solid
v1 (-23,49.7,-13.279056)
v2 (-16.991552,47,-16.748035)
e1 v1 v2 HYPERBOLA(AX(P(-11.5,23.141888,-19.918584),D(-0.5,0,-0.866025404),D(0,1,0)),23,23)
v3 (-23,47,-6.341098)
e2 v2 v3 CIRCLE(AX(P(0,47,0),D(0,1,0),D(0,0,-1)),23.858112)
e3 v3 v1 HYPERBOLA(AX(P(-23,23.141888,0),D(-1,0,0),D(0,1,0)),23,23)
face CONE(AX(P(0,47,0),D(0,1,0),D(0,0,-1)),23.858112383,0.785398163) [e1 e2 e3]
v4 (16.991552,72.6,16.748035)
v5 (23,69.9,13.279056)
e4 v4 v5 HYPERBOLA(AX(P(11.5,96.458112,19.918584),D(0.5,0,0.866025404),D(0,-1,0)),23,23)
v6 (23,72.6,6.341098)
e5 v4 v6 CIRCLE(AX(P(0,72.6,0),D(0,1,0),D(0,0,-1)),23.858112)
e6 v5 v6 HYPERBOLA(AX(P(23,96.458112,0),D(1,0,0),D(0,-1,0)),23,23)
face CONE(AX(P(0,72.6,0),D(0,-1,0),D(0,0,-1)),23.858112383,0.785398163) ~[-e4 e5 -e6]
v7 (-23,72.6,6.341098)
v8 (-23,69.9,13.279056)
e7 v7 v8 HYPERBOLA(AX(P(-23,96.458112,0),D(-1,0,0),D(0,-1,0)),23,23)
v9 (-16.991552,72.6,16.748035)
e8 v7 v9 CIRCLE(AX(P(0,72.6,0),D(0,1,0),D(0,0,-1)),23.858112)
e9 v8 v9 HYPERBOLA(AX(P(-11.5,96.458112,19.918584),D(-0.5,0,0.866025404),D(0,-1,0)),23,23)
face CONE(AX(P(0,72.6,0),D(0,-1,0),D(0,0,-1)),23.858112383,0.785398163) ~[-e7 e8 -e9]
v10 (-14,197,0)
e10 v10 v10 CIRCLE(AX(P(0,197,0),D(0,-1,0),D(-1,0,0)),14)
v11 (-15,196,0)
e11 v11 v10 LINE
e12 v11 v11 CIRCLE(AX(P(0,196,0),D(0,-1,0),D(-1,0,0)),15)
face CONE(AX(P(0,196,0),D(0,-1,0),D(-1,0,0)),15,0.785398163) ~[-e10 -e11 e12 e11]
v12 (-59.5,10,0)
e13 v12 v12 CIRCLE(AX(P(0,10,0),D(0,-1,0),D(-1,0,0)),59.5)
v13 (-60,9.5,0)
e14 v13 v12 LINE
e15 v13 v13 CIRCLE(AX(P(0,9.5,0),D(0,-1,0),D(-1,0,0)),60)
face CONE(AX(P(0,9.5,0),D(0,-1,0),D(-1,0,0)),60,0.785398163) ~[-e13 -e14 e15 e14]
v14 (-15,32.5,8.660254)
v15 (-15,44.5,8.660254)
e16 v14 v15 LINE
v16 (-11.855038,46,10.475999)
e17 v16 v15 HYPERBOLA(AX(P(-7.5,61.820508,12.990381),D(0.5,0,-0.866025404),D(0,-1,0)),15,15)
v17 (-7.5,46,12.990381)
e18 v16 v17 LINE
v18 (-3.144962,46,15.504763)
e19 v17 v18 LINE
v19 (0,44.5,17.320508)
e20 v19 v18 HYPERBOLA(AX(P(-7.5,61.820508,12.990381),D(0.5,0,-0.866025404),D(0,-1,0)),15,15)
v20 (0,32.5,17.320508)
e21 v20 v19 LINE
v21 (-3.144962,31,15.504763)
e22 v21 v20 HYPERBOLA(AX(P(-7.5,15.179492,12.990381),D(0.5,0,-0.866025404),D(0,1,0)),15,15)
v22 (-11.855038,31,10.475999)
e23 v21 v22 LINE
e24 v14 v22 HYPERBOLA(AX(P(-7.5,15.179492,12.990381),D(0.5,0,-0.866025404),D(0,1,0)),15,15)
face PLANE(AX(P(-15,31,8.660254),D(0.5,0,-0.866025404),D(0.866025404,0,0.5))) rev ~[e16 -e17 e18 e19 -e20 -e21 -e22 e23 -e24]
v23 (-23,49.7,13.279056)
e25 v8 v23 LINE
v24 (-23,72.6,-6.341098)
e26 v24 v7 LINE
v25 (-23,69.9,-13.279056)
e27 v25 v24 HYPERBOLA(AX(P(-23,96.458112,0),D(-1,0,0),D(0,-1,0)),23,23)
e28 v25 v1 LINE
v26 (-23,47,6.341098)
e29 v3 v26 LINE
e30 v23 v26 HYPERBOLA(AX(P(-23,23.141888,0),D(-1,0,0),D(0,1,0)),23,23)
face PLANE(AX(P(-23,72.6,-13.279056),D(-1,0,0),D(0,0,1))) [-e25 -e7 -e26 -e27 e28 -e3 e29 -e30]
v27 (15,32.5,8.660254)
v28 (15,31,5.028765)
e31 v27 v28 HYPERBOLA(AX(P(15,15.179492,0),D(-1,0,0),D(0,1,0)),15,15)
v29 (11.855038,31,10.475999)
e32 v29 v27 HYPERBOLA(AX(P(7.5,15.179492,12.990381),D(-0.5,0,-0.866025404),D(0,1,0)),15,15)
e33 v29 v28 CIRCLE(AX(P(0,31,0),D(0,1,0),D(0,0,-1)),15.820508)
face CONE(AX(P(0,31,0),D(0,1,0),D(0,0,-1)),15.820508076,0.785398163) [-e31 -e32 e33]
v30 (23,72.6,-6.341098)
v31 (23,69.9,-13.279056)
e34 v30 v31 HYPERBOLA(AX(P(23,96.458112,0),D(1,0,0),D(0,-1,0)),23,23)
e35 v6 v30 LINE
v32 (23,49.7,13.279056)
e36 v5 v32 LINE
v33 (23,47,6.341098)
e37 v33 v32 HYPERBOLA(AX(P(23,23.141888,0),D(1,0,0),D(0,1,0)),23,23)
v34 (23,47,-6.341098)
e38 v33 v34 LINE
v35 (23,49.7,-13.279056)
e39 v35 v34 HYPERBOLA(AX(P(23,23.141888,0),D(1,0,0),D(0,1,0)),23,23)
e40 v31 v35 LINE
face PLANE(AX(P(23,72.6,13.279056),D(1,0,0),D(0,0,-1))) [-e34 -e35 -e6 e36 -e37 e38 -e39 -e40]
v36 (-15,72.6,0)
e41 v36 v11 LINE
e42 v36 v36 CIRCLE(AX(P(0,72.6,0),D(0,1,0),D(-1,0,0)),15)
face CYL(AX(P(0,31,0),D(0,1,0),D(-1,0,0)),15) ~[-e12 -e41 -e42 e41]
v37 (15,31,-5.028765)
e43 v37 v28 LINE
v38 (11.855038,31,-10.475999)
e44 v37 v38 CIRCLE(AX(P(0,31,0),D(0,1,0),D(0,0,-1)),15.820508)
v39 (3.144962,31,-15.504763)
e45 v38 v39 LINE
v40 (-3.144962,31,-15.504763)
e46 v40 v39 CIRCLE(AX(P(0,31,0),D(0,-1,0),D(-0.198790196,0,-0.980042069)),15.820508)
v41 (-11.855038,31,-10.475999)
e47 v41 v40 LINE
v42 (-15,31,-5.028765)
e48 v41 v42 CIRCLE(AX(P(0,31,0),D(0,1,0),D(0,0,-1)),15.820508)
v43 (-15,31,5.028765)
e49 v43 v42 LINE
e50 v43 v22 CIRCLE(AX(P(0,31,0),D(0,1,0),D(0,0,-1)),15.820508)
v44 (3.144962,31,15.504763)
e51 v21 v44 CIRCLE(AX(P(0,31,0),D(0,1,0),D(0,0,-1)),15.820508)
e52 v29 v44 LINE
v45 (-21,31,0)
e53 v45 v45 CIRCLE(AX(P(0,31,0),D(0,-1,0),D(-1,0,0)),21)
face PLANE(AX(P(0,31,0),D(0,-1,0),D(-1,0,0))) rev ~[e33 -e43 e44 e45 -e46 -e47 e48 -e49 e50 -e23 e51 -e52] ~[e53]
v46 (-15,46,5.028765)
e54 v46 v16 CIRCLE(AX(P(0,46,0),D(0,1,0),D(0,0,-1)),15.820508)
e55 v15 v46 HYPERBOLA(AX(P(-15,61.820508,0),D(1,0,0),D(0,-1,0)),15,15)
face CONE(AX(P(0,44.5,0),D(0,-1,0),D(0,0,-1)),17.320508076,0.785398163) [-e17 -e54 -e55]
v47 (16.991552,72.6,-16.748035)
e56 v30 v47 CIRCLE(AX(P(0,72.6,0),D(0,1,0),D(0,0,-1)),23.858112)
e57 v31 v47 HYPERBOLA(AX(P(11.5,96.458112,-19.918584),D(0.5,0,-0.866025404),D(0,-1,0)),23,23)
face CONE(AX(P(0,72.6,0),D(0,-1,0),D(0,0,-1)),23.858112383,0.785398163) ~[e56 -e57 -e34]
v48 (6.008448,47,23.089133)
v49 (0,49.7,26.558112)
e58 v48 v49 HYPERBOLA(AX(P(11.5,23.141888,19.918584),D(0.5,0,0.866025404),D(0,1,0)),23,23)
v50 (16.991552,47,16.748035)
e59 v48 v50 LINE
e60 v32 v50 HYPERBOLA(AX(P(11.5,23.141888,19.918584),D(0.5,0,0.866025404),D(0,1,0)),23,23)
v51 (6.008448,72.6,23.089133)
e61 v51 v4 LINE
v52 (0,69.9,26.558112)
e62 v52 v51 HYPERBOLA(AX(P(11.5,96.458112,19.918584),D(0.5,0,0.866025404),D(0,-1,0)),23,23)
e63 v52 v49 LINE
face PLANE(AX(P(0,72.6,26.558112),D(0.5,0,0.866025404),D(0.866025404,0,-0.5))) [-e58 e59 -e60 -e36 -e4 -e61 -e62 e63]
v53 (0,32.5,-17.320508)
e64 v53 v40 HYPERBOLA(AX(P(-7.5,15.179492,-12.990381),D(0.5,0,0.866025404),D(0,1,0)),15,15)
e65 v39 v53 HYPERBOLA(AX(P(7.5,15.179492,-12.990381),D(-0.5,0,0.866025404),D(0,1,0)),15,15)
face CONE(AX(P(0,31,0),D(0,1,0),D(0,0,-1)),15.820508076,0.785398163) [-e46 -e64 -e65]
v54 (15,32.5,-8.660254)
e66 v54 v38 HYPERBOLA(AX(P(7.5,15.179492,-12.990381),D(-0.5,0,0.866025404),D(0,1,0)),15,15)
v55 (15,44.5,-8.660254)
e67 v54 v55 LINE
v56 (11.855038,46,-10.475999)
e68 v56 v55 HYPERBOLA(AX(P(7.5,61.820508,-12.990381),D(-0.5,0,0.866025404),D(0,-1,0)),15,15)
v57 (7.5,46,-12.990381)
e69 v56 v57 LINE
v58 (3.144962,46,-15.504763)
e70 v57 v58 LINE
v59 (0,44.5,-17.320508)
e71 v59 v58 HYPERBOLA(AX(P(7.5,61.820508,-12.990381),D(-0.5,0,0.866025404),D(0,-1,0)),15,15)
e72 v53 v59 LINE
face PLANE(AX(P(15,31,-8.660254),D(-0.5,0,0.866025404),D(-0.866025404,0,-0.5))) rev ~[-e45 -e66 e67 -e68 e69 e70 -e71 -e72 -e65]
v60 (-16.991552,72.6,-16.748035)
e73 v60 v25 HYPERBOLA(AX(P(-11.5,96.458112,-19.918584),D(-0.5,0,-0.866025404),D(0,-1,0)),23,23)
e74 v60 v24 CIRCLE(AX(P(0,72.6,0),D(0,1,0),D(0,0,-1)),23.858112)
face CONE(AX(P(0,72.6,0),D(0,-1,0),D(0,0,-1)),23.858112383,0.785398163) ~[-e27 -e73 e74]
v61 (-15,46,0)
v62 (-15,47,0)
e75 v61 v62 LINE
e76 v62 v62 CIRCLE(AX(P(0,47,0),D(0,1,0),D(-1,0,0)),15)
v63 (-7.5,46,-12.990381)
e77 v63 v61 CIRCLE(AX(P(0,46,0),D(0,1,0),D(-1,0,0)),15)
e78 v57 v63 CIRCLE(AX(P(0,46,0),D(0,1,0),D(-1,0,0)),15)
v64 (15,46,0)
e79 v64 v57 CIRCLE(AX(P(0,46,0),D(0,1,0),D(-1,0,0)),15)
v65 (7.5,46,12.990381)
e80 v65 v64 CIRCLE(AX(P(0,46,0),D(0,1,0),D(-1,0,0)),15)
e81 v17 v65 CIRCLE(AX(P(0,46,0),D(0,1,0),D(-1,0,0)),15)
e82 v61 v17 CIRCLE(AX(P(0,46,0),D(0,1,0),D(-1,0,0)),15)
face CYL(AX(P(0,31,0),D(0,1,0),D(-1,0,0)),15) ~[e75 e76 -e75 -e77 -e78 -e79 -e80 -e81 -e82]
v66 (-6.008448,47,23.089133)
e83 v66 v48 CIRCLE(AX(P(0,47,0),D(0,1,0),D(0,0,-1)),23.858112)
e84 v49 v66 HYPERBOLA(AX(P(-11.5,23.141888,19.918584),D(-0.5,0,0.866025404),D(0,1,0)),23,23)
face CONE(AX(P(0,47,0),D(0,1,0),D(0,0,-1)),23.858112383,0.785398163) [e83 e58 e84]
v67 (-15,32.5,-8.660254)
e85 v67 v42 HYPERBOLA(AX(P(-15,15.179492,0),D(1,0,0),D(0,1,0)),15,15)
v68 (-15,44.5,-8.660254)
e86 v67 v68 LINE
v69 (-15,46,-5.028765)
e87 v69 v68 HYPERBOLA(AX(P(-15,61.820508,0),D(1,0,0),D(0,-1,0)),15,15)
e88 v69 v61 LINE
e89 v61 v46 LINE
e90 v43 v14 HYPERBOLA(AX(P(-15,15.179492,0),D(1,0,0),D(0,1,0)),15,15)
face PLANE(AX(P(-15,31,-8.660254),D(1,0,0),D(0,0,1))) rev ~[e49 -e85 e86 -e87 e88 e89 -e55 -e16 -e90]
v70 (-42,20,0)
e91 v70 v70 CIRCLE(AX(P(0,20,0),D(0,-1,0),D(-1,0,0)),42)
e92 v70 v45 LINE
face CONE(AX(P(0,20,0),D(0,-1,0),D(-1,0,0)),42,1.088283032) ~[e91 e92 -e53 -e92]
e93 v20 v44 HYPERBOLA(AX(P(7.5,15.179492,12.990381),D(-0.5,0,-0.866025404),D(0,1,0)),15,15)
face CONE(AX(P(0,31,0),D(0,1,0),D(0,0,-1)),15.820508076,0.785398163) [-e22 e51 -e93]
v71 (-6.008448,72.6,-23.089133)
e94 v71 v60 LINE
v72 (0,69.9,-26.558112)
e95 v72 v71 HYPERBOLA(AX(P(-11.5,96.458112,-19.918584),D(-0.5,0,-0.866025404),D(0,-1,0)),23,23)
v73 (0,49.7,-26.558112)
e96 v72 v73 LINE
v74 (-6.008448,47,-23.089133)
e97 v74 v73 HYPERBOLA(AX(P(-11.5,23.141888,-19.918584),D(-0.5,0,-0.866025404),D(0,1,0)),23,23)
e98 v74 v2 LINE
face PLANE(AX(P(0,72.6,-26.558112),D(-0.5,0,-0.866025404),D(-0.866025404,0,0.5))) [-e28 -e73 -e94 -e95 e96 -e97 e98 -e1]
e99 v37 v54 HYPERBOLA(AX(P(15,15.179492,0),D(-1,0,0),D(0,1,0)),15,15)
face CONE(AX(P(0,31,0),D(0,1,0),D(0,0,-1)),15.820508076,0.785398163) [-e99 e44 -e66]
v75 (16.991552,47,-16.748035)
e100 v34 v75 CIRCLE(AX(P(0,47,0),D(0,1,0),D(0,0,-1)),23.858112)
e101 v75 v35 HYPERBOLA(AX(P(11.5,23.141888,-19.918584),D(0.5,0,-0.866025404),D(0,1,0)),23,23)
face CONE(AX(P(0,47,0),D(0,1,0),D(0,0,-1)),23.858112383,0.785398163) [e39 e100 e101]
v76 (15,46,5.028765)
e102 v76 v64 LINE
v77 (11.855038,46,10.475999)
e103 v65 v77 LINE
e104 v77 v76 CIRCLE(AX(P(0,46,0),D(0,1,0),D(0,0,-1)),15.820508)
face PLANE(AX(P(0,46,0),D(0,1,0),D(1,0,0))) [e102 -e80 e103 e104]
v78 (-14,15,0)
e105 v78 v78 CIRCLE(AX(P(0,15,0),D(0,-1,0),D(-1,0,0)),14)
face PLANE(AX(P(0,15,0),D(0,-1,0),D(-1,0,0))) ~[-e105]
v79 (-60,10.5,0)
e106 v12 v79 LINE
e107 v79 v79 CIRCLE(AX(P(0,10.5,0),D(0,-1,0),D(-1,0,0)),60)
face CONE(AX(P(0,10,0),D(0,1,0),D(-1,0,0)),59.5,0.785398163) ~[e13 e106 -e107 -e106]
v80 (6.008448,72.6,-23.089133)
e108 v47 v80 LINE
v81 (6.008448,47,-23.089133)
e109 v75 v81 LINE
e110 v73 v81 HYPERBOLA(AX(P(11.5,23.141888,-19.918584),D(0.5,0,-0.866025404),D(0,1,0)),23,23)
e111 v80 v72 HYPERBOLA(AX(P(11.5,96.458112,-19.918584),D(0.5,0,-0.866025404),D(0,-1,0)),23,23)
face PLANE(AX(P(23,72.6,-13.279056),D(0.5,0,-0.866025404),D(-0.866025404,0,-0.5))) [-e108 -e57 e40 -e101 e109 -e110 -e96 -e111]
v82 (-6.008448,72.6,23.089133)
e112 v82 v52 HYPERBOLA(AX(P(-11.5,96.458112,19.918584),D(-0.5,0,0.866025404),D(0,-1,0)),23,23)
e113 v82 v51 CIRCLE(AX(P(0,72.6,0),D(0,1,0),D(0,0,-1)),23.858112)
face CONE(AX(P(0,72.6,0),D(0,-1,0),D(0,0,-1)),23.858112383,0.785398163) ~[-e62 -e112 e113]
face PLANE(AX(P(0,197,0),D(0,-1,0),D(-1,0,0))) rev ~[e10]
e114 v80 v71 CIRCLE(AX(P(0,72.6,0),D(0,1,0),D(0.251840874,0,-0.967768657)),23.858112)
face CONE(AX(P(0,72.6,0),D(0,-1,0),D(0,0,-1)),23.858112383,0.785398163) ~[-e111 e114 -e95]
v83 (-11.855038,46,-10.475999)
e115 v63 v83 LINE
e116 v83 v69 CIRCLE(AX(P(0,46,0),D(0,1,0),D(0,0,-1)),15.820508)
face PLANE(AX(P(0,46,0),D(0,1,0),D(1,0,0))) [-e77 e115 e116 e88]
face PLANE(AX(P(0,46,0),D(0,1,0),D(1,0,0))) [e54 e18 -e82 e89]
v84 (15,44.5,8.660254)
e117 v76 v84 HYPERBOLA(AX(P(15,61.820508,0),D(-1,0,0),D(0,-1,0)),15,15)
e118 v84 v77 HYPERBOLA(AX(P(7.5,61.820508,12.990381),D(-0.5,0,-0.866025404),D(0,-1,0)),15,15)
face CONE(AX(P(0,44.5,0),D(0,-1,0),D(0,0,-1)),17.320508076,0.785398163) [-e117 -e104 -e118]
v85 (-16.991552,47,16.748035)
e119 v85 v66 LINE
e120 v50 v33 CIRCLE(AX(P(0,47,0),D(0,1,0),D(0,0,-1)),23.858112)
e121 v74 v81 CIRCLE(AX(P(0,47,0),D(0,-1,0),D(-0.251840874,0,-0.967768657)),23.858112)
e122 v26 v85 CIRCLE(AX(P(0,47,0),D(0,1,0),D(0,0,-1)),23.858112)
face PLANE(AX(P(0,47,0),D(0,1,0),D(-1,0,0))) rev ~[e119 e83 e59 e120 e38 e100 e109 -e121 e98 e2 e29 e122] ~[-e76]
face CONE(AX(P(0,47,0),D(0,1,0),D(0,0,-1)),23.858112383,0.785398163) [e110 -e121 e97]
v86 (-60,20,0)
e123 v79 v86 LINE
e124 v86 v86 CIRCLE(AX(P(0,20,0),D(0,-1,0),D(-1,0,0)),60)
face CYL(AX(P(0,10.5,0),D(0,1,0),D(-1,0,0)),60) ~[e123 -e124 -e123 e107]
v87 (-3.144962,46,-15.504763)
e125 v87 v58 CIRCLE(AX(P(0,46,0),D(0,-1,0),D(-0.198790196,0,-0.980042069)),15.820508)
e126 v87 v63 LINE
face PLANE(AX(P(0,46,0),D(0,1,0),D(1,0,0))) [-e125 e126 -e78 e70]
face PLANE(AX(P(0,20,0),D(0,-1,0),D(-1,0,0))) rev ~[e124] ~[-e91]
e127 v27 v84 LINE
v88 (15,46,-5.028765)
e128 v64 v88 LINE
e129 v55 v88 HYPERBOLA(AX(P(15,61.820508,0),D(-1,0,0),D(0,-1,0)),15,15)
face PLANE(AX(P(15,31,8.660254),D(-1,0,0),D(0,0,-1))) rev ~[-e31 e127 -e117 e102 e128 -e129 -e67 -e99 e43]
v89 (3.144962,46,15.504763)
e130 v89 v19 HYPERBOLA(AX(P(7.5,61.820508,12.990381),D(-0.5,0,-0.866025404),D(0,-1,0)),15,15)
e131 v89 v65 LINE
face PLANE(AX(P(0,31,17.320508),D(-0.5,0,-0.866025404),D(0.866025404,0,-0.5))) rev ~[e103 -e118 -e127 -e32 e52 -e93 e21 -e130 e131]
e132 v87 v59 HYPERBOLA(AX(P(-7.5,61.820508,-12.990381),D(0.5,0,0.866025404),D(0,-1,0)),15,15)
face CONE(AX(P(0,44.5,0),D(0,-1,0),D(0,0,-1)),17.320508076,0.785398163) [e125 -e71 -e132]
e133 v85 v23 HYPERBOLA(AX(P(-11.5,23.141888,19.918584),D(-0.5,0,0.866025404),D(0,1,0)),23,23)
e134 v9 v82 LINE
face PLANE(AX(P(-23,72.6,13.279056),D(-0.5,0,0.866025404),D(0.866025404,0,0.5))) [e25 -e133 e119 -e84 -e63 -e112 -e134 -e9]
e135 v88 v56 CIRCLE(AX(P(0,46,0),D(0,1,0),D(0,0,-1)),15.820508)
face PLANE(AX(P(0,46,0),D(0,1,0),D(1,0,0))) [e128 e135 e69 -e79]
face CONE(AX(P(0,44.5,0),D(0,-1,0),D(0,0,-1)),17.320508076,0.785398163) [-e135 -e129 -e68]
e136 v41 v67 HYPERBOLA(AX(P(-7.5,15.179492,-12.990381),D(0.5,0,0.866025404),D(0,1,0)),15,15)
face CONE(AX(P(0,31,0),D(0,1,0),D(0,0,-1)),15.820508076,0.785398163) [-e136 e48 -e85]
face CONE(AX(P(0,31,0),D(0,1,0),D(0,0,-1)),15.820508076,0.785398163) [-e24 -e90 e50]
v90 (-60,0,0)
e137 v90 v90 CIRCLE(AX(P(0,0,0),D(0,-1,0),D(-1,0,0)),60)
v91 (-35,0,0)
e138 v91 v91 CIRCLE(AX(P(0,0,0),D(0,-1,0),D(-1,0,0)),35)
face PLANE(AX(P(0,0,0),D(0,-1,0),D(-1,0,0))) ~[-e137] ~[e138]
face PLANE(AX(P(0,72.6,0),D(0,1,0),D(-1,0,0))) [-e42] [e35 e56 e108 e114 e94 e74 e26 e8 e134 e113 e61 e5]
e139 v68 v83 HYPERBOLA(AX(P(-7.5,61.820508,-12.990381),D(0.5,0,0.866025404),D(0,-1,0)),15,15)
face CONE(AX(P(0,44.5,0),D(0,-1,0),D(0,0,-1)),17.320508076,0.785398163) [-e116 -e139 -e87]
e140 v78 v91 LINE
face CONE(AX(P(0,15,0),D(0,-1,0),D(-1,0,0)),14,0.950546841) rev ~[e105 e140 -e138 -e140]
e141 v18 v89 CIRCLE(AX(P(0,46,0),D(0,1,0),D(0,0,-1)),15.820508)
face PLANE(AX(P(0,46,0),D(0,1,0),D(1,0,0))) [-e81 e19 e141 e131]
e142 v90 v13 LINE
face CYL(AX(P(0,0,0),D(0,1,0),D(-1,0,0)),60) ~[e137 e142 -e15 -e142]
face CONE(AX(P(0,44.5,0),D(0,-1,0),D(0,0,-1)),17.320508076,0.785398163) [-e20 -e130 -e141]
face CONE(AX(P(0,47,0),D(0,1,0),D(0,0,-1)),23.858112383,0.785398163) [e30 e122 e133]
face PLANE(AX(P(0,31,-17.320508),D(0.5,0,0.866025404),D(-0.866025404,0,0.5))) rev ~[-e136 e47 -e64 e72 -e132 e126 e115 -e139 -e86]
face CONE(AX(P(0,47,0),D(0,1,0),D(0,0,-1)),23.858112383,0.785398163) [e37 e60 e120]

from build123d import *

# Parameters (mm, degrees)
BOSS_EXTRUDE1_DEPTH = 15
BOSS_EXTRUDE2_START = 25.6
SKETCH5_R           = 15
BOSS_EXTRUDE2_DEPTH = 25.6
CHAMFER1_SIZE       = 1


with BuildPart() as part:
    # Sketch1 → Revolve1 (revolve)
    with BuildSketch(Plane.XY, mode=Mode.PRIVATE) as revolve1_sk:
        Polygon((35, 0), (60, 0), (60, 9.5), (59.5, 10), (60, 10.5), (60, 20), (42, 20), (21, 31), (15, 31), (15, 197), (0, 197), (0, 15), (14, 15), align=None)
    revolve(revolve1_sk.sketch.rotate(Axis((0, 197, 0), (0, -1, 0)), 180), axis=Axis((0, 197, 0), (0, -1, 0)))

    # Sketch2 → Boss-Extrude1 (add)
    with BuildSketch(Plane(origin=(0, 31, 0), x_dir=(1, 0, 0), z_dir=(0, 1, 0))):
        Polygon((15, 8.660254038), (0, 17.320508076), (-15, 8.660254038), (-15, -8.660254038), (0, -17.320508076), (15, -8.660254038), align=None)
    extrude(amount=BOSS_EXTRUDE1_DEPTH)

    # Sketch3 → Cut-Revolve1 (revolve, cut)
    with BuildSketch(Plane(origin=(0, 0, 0), x_dir=(0, 0, -1), z_dir=(1, 0, 0))):
        Polygon((15.820508076, 31), (17.320508076, 32.5), (17.320508076, 31), align=None)
        Polygon((17.320508076, 44.5), (15.820508076, 46), (17.320508076, 46), align=None)
    revolve(axis=Axis((0, 197, 0), (0, 1, 0)), mode=Mode.SUBTRACT)

    # Sketch5 → Boss-Extrude2 (add)
    with BuildSketch(Plane(origin=(0, 47, 0), x_dir=(-1, 0, 0), z_dir=(0, 1, 0)).offset(BOSS_EXTRUDE2_START)):
        Polygon((0, 26.558112383), (-23, 13.279056191), (-23, -13.279056191), (0, -26.558112383), (23, -13.279056191), (23, 13.279056191), align=None)
        Circle(SKETCH5_R, mode=Mode.SUBTRACT)
    extrude(amount=-BOSS_EXTRUDE2_DEPTH)

    # Sketch7 → Cut-Revolve3 (revolve, cut)
    with BuildSketch(Plane(origin=(0, 0, 0), x_dir=(0, 0, -1), z_dir=(1, 0, 0))):
        Polygon((23.858112383, 72.6), (26.558112383, 69.9), (26.558112383, 72.6), align=None)
        Polygon((23.858112383, 47), (26.558112383, 49.7), (26.558112383, 47), align=None)
    revolve(axis=Axis((0, 197, 0), (0, 1, 0)), mode=Mode.SUBTRACT)

    # Chamfer1
    chamfer1_edges = [part.edges().sort_by_distance(p)[0] for p in [
        (15, 197, 0),
    ]]
    chamfer(chamfer1_edges, length=CHAMFER1_SIZE)


solid = part.part
